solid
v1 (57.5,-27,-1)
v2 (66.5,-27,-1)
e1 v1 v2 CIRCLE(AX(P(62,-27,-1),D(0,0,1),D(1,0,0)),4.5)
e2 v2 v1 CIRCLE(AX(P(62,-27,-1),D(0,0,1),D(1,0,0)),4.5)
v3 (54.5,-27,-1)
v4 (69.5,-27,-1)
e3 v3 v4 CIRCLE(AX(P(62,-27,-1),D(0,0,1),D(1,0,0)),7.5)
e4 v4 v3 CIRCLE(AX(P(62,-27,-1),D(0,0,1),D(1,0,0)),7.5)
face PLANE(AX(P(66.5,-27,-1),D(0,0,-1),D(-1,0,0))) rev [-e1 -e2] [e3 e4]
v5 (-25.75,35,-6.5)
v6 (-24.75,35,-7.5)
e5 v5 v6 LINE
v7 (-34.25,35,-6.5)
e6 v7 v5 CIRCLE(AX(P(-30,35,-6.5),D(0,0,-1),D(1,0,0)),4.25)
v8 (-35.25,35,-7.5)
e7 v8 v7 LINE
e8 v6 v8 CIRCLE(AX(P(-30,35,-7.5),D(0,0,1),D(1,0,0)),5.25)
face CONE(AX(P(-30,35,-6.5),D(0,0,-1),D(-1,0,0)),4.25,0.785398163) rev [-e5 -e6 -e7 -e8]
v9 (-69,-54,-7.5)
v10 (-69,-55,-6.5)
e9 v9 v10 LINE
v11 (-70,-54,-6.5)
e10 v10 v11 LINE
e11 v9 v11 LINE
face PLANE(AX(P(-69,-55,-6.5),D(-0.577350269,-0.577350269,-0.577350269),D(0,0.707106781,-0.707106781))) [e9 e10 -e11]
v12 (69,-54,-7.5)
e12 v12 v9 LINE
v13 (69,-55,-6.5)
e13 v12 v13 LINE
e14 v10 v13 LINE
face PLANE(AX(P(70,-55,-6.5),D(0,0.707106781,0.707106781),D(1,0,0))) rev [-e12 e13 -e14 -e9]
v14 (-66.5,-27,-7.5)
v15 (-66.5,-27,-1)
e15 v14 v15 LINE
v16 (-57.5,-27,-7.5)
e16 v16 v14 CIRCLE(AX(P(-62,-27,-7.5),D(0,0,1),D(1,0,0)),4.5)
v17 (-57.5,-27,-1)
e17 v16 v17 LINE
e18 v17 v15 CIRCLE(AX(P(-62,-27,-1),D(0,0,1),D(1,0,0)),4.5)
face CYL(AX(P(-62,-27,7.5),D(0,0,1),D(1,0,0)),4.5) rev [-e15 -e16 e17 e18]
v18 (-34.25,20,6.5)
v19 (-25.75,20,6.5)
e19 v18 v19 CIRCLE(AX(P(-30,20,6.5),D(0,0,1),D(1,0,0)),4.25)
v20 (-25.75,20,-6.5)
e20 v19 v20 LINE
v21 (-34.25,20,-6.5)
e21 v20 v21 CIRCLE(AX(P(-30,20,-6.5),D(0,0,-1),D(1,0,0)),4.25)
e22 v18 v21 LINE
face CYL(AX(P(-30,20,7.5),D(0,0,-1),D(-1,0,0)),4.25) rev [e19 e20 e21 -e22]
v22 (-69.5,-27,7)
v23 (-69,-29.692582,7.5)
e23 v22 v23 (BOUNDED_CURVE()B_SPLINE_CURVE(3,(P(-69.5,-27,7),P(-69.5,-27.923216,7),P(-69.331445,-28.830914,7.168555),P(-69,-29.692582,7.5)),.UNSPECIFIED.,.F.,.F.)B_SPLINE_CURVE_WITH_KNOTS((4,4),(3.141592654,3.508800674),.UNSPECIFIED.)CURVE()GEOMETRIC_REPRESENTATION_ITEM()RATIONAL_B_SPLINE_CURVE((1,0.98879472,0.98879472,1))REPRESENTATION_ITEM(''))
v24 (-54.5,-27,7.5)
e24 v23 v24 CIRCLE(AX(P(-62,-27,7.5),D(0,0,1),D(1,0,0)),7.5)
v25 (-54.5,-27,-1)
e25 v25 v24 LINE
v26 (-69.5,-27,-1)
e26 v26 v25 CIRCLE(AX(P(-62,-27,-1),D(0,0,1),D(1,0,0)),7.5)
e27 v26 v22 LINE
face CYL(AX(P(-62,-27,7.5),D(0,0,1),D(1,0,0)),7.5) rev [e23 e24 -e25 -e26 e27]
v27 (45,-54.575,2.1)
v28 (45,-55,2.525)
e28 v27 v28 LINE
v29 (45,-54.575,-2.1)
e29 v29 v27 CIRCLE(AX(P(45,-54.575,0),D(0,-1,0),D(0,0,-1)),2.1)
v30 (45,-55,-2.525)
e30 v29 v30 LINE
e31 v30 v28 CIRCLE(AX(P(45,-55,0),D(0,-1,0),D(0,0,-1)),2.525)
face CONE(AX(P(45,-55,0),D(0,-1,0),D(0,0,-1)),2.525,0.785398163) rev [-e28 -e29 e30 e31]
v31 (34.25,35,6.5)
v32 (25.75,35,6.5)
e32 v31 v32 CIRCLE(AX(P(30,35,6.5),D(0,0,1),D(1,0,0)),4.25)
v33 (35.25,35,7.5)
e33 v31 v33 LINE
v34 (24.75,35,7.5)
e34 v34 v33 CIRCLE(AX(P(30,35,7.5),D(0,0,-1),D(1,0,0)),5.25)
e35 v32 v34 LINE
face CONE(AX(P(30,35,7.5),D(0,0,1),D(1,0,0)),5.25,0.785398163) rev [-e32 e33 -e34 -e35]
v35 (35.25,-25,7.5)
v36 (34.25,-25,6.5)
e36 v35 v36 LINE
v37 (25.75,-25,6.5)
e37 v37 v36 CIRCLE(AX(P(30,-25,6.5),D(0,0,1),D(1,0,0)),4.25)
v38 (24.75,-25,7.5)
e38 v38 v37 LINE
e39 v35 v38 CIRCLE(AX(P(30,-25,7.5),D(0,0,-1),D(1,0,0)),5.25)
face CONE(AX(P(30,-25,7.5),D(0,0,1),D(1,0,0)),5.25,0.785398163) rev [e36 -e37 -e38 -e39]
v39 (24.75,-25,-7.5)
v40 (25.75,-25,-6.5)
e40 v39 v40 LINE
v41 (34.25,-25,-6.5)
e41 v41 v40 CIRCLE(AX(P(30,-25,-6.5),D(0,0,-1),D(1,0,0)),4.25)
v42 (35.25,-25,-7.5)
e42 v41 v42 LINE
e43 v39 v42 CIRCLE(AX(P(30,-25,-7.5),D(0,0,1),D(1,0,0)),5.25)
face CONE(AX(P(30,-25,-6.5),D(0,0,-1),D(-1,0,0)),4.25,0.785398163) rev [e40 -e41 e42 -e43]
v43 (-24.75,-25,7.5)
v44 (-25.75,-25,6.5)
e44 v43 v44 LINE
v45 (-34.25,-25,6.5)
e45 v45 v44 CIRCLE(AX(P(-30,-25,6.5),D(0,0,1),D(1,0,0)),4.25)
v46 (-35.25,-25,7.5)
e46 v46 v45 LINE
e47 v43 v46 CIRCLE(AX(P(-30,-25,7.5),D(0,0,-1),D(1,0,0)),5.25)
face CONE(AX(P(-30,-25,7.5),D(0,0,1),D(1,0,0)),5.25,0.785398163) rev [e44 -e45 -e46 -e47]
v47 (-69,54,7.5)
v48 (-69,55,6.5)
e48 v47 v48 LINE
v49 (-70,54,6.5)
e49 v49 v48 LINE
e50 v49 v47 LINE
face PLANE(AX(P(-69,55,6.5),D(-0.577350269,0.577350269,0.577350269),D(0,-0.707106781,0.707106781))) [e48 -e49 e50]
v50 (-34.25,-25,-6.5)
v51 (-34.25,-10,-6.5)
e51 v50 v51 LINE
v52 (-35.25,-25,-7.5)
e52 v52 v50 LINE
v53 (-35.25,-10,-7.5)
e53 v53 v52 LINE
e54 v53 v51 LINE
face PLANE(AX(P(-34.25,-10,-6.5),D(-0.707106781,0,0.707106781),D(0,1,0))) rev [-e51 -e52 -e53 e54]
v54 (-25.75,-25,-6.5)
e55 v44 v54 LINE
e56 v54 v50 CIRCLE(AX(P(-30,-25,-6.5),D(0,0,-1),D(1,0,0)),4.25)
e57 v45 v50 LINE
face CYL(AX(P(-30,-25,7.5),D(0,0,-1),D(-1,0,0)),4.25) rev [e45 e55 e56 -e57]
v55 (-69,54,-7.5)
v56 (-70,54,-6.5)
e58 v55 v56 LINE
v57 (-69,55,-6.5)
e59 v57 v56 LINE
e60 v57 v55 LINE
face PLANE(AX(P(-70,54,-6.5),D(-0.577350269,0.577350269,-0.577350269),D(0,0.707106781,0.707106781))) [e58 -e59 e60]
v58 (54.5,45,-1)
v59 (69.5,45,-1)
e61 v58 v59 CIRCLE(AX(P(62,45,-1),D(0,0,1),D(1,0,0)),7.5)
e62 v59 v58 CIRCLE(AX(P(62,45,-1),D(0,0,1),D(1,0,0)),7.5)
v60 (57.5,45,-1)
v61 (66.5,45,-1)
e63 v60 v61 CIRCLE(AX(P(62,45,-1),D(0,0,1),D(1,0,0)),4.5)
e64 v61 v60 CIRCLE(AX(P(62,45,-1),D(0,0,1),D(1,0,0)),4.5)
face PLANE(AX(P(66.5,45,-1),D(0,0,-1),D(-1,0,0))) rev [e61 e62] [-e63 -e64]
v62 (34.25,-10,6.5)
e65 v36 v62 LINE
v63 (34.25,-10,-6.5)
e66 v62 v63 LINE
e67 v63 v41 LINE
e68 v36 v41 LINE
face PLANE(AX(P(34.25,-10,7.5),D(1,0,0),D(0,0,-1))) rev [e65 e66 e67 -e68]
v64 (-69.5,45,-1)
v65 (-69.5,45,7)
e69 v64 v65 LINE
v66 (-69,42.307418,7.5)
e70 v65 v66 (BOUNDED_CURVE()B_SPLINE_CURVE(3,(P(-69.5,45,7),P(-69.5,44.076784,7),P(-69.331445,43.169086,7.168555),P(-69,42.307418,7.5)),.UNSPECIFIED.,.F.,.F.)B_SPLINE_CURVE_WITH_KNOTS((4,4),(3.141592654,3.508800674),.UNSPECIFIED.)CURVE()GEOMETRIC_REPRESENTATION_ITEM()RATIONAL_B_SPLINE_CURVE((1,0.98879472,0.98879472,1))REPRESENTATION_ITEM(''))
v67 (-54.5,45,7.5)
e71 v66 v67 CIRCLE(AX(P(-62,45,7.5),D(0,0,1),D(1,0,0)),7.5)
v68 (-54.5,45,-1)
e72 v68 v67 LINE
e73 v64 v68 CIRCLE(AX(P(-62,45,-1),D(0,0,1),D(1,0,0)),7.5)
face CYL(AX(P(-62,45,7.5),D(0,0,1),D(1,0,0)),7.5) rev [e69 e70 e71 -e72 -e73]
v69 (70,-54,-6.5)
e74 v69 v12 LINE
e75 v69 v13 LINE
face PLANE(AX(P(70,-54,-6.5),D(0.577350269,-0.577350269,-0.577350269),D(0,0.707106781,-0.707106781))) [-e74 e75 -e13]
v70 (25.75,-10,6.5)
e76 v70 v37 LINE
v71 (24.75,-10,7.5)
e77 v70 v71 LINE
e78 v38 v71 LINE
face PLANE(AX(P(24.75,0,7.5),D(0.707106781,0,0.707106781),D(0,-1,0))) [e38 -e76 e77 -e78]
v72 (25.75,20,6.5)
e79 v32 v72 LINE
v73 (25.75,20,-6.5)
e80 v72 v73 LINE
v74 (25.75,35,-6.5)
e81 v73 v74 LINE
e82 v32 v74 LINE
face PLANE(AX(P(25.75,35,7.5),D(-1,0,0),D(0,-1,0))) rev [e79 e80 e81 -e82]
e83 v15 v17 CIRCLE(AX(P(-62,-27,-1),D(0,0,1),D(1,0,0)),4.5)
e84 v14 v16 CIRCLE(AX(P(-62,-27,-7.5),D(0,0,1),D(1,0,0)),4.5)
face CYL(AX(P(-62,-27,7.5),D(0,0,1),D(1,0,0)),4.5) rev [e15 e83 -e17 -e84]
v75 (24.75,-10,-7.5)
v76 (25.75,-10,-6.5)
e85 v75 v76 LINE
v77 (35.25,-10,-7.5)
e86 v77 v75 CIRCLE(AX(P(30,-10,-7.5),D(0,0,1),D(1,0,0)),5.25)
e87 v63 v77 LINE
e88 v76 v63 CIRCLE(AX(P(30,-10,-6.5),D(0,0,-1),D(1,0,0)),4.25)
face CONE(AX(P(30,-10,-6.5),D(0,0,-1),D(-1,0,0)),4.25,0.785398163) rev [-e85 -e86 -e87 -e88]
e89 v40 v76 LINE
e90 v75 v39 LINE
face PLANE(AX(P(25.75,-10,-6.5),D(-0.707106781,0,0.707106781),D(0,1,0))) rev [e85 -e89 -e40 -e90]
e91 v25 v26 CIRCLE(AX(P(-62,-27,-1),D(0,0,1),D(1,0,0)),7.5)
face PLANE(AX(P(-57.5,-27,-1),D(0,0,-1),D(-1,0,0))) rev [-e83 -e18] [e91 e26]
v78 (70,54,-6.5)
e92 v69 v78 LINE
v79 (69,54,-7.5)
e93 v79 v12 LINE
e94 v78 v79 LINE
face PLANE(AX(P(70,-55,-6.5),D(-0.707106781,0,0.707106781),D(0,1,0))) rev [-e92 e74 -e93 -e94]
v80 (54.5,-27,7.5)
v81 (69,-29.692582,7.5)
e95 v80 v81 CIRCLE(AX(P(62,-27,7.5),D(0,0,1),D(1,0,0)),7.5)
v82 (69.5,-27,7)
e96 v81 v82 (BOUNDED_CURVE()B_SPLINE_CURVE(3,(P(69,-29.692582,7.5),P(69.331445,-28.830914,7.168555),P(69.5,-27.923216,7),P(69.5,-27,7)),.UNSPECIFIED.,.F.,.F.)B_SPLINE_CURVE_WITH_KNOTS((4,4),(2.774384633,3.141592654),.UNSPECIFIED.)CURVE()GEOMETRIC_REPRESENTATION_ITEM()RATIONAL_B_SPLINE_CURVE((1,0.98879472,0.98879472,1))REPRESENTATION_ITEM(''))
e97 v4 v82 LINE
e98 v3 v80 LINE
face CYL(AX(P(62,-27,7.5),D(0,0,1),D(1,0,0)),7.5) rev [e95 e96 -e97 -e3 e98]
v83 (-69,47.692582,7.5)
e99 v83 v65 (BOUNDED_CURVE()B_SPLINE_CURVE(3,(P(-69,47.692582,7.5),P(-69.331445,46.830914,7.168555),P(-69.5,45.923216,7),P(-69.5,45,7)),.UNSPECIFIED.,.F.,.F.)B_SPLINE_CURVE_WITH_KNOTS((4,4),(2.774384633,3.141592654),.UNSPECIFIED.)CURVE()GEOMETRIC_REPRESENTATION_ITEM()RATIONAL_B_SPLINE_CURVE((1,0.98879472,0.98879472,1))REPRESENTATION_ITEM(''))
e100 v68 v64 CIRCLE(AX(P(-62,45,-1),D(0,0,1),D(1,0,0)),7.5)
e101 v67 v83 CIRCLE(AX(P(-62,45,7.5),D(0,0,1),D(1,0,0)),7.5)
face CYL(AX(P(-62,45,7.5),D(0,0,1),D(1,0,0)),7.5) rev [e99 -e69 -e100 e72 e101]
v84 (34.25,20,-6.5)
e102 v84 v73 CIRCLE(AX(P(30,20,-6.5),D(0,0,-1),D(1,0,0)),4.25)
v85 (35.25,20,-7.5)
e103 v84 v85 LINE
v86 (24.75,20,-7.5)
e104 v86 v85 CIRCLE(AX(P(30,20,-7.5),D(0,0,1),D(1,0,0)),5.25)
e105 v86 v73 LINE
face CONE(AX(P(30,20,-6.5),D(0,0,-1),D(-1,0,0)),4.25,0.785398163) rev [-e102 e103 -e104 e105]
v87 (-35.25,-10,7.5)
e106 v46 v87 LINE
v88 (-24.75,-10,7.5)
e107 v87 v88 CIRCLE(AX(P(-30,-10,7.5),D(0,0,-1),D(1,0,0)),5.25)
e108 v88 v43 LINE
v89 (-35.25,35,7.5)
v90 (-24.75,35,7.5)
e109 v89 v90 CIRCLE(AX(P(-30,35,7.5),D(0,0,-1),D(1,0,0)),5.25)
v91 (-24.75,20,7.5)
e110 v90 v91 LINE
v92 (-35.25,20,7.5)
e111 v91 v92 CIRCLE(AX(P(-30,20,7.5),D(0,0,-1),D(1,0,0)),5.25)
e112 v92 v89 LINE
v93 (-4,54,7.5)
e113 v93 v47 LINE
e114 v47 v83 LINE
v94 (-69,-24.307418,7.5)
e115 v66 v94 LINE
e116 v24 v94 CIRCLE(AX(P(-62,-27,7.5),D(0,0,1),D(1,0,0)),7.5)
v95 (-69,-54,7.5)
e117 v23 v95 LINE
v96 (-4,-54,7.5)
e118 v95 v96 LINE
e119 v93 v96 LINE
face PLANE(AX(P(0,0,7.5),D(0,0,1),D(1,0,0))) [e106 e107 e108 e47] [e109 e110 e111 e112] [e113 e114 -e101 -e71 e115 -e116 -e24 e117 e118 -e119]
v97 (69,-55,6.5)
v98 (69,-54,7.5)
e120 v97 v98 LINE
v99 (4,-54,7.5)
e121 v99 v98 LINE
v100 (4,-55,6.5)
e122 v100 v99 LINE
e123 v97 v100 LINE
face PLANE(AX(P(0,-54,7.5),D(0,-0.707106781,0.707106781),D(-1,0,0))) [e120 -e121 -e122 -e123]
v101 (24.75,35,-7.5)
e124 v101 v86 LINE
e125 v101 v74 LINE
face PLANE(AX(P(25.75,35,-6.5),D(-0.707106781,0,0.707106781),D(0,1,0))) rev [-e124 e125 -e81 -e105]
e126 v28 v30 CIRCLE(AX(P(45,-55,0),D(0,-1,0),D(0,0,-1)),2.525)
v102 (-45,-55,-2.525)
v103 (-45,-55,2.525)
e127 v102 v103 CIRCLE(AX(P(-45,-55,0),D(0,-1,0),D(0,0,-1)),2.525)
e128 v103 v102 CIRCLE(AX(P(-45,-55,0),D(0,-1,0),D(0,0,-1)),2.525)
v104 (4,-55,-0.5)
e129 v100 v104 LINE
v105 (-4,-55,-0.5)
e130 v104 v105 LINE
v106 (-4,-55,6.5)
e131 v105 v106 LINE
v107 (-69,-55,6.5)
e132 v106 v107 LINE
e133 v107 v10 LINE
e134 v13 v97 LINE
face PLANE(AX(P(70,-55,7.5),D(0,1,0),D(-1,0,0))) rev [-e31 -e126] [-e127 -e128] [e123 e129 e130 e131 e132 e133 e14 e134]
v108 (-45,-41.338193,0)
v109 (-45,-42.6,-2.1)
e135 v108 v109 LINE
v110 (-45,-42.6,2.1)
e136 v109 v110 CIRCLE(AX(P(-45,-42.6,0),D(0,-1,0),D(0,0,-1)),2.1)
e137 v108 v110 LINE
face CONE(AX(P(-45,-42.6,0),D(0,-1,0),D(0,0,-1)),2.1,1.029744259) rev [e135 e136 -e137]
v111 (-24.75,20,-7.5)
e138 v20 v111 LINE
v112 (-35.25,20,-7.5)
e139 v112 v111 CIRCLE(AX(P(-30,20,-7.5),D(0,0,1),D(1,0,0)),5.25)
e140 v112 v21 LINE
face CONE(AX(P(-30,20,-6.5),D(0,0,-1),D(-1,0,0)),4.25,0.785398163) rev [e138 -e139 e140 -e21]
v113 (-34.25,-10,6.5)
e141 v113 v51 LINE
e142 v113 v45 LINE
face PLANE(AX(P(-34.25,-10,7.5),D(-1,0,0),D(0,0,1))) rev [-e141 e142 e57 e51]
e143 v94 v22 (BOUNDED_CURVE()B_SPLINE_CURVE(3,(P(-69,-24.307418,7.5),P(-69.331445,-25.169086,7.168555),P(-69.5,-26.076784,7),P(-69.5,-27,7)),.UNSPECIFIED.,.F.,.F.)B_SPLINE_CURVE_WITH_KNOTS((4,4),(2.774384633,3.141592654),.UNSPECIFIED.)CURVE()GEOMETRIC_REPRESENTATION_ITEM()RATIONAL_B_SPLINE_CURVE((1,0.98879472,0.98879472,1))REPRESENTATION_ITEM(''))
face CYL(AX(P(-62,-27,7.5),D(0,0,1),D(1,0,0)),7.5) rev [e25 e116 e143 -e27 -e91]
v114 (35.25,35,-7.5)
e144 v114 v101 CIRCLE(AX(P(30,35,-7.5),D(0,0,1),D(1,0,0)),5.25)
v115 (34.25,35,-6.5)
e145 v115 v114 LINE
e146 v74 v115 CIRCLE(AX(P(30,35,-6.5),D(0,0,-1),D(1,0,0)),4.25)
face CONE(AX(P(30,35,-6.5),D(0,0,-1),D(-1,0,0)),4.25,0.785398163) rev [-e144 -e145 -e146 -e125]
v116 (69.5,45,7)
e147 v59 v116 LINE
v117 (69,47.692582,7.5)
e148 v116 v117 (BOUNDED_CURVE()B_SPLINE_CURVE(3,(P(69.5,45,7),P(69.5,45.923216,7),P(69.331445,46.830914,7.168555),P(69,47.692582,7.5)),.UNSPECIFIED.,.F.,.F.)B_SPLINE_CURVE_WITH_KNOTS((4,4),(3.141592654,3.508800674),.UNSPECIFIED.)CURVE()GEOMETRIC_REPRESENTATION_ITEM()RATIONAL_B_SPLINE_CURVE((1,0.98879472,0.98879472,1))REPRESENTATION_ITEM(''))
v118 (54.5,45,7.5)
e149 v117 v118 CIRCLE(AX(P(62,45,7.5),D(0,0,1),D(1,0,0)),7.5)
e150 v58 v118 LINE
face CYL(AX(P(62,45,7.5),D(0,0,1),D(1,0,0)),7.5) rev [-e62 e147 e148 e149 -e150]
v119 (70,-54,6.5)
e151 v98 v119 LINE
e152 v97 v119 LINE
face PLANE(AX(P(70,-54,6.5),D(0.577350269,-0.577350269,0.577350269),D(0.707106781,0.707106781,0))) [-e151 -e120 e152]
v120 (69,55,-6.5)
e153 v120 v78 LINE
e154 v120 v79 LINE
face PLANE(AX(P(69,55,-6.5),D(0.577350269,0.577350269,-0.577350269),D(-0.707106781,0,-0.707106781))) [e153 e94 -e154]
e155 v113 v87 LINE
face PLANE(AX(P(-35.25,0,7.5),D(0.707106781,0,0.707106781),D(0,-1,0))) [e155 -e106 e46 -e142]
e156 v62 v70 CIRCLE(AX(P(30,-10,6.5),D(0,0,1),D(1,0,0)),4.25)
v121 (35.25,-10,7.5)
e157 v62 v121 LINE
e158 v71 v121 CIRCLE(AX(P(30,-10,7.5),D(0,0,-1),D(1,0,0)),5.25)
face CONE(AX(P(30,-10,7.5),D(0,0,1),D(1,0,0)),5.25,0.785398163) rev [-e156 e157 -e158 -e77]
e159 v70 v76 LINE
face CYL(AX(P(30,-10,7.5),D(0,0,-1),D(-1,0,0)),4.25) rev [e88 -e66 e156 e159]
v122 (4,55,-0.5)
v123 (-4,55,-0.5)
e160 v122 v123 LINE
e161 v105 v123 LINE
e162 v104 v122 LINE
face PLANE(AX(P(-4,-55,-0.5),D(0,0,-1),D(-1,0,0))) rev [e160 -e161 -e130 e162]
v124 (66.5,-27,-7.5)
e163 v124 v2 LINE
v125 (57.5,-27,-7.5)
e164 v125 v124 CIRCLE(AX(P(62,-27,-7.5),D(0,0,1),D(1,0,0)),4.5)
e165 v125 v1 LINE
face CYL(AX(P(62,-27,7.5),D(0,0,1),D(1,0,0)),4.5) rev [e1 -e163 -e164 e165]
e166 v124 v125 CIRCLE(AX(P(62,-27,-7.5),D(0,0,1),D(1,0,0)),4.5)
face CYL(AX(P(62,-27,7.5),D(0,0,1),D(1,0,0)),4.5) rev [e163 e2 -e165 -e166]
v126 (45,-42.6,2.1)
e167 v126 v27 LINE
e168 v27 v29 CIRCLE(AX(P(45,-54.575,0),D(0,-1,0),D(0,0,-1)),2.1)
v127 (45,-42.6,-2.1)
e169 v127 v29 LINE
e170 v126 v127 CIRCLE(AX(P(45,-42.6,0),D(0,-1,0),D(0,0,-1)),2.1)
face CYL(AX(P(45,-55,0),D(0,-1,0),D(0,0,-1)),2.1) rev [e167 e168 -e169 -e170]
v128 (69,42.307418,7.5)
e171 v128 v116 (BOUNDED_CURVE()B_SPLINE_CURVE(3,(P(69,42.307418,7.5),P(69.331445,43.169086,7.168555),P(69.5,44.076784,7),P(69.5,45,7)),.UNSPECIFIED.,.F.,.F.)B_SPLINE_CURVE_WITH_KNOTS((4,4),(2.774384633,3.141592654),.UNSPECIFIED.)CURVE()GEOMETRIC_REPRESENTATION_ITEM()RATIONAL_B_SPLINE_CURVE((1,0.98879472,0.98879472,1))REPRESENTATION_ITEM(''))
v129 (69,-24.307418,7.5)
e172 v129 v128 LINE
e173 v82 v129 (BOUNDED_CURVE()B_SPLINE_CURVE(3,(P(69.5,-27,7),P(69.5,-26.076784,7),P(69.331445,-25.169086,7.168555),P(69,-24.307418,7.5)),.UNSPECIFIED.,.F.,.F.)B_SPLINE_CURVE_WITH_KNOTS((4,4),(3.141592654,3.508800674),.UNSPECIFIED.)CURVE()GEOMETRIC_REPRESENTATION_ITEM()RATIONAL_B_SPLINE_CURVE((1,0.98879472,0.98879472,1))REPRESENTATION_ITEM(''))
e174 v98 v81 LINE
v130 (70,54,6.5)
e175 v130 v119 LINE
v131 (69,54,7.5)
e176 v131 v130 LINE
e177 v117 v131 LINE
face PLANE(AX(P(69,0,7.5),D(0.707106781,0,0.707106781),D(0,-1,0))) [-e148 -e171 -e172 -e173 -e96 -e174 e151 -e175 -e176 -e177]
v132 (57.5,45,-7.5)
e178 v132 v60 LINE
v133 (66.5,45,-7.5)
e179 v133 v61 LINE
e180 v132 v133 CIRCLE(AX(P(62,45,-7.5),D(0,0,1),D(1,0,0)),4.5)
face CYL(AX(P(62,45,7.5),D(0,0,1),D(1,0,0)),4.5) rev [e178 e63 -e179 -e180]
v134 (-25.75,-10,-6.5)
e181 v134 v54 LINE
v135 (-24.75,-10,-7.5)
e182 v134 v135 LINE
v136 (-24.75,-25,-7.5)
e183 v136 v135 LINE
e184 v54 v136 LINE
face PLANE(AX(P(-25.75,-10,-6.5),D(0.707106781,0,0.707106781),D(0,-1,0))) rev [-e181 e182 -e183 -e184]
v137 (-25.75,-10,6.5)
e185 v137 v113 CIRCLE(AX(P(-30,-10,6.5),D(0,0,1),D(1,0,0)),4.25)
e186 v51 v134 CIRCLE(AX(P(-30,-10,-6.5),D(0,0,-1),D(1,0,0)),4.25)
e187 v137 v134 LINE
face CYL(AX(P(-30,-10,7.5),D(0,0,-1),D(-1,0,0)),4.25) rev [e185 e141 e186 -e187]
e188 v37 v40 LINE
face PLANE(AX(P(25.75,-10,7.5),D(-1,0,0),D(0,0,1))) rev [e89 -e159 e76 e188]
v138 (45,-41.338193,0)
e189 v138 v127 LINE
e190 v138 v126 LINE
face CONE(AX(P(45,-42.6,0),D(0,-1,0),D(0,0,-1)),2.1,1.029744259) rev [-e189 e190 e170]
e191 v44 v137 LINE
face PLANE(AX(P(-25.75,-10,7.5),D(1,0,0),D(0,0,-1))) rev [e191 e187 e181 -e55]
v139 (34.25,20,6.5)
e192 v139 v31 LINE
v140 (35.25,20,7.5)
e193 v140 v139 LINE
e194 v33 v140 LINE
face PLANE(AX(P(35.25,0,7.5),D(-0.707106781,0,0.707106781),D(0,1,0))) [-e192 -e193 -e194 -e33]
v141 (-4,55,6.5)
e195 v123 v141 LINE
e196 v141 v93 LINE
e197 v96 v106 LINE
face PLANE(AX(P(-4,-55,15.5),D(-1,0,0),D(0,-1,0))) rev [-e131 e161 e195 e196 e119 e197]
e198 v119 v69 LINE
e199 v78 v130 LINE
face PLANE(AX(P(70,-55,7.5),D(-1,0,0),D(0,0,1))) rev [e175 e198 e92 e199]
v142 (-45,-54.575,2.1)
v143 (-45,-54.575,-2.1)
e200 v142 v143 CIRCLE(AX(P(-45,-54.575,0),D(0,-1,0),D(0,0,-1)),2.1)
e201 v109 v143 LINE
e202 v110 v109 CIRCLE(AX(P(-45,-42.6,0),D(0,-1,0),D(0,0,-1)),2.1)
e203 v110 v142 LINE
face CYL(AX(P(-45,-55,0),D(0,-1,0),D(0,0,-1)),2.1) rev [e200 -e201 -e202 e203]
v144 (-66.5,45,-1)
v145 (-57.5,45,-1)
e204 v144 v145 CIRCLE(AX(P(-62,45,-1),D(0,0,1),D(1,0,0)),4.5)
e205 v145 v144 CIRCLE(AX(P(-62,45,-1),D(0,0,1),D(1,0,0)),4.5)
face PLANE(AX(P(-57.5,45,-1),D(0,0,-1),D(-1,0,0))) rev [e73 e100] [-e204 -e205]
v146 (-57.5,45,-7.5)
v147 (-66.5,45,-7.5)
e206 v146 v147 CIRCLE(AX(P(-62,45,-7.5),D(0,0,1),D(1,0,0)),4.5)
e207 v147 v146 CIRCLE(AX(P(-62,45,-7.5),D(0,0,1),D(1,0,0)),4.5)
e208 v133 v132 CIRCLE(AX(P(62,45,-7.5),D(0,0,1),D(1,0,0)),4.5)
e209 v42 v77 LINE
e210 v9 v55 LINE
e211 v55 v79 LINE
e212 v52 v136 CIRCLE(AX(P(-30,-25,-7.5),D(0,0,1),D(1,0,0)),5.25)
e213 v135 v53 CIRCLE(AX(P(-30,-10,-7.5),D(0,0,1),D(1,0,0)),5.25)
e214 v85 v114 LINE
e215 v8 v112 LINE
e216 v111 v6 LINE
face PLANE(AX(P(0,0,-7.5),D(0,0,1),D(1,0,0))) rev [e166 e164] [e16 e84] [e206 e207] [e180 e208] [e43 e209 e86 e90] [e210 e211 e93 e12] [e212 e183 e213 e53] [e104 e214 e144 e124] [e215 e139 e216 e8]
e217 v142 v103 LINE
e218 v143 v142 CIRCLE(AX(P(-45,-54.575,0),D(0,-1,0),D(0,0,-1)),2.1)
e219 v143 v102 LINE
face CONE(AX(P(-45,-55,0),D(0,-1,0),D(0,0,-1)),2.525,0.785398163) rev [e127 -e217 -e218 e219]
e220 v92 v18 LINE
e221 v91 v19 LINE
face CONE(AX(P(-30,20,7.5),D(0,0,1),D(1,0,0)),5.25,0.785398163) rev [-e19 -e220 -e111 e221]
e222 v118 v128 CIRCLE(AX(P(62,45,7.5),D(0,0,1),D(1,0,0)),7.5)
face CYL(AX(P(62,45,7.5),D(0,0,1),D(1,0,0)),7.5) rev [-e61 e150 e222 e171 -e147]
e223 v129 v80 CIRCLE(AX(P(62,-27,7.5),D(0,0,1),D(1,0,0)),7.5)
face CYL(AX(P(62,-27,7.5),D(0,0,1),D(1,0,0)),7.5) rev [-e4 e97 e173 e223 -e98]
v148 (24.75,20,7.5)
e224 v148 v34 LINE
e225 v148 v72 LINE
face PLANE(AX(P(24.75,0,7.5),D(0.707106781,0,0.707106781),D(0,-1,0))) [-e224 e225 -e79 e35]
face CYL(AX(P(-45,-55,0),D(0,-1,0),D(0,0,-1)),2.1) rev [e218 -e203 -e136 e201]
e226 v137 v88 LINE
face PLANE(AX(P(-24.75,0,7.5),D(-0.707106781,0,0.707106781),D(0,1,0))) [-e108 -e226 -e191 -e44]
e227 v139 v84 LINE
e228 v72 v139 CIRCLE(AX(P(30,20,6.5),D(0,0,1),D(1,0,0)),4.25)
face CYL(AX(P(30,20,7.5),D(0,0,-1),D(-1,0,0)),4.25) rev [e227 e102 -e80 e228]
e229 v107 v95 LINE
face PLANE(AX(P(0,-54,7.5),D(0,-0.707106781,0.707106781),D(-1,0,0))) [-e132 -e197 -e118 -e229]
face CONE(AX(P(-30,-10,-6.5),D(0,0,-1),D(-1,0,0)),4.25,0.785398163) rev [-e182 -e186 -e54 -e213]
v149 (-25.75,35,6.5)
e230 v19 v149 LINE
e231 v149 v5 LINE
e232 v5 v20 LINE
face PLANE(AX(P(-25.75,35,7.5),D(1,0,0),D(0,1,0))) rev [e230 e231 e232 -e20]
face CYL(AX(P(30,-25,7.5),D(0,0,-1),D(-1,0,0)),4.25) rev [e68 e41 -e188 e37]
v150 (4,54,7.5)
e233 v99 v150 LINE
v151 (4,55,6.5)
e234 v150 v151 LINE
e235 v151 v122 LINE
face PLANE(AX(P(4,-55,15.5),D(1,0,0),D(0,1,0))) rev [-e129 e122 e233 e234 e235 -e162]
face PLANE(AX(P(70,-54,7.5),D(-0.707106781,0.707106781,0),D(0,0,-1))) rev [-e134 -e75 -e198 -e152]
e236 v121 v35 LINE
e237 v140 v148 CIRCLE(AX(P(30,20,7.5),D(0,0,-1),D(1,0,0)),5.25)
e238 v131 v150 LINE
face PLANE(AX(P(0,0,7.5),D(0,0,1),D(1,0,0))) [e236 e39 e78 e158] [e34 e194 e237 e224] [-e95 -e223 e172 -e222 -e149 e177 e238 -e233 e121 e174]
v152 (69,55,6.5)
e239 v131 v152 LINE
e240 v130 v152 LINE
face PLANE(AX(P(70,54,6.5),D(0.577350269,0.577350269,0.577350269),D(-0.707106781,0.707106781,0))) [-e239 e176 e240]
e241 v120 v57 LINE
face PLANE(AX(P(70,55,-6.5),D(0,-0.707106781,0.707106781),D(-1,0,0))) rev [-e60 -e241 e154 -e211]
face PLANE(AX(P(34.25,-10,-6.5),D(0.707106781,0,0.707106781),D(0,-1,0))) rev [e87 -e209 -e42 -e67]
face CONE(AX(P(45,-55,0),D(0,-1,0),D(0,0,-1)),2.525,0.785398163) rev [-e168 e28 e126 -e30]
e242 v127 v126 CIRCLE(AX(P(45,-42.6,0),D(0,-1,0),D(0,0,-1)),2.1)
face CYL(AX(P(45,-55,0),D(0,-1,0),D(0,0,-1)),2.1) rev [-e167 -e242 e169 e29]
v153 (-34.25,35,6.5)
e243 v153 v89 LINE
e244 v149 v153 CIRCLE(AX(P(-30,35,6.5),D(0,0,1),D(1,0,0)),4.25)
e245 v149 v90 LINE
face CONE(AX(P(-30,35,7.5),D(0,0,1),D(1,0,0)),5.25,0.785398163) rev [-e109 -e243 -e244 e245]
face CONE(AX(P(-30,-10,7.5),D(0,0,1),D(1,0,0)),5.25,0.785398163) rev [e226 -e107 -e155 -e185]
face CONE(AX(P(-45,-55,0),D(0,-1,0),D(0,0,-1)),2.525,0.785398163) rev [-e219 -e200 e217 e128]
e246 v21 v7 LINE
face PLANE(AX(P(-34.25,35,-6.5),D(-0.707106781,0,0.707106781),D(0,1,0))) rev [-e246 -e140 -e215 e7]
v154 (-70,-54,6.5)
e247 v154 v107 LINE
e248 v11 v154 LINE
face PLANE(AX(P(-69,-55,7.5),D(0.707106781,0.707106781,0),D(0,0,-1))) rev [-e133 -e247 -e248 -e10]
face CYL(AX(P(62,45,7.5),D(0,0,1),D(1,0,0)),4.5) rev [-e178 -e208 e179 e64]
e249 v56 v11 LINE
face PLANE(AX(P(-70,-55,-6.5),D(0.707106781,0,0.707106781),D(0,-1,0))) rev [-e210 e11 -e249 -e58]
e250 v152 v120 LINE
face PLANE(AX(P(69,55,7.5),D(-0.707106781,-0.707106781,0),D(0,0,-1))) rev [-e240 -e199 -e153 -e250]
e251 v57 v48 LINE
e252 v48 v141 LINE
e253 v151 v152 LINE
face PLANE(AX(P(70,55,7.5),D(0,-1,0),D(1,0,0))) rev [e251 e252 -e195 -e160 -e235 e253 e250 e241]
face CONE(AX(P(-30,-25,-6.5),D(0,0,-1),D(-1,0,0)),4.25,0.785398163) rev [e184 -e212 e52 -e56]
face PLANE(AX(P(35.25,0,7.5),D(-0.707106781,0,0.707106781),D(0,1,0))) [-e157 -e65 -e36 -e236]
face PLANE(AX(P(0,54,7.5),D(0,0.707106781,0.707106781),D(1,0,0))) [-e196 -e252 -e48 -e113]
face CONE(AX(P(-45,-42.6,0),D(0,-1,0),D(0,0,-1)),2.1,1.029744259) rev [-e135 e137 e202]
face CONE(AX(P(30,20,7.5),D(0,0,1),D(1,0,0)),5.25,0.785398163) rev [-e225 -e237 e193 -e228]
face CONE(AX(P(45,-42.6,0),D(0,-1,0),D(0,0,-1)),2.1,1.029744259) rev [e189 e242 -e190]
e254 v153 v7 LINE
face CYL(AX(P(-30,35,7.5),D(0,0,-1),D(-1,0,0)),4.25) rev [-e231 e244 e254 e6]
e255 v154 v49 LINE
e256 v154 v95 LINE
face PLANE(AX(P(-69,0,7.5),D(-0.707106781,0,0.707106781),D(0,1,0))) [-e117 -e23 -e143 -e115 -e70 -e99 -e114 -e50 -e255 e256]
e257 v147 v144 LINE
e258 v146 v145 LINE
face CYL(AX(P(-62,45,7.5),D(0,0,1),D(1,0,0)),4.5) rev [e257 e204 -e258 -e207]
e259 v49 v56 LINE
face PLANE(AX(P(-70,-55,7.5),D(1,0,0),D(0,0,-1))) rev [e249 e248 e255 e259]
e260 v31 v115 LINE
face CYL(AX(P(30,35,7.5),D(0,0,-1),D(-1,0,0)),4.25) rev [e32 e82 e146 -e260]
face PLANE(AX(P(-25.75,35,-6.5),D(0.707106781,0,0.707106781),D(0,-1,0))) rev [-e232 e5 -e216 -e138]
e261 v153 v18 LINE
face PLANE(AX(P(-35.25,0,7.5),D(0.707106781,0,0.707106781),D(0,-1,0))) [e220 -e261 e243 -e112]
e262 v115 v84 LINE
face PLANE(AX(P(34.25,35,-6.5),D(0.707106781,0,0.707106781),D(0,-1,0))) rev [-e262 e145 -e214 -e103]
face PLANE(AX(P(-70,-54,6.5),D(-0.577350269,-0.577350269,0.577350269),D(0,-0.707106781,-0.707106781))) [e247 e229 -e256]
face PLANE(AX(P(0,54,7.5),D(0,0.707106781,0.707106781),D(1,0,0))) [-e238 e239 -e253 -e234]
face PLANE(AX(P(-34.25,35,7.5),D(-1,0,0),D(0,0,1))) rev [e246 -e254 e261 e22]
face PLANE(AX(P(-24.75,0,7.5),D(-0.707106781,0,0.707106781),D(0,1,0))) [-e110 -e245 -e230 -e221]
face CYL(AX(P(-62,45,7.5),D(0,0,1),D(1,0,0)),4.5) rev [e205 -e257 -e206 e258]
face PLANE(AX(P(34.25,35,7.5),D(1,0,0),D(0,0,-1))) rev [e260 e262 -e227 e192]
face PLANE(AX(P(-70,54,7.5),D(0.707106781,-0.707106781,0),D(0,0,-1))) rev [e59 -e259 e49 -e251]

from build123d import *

# Parameters (mm, degrees)
SKETCH_1_W                   = 140
SKETCH_1_H                   = 110
EXTRUDE_1_DEPTH              = 7.5
CUT_EXTRUDE_1_DEPTH          = 91.277350426
CHAMFER_2_SIZE               = 1
SKETCH_5_W                   = 8
SKETCH_5_H                   = 16
CUT_EXTRUDE_2_DEPTH          = 131.599578866
HOLE_WIZARD_M5_1_D           = 4.2
HOLE_WIZARD_M5_2_D           = 4.2
HOLE_WIZARD_M5_2_DEPTH       = 12.4
HOLE_WIZARD_M5_2_CSINK_D     = 5.05
HOLE_WIZARD_M5_2_CSINK_ANGLE = 90
HOLE_WIZARD_M5_2_TIP         = 1.2618073
HOLE1_D                      = 9
HOLE1_CBORE_D                = 15
HOLE1_CBORE_DEPTH            = 8.5


with BuildPart() as part:
    # 草图1 → 凸台-拉伸1 (new, symmetric)
    with BuildSketch(Plane.XY):
        Rectangle(SKETCH_1_W, SKETCH_1_H)
    extrude(amount=EXTRUDE_1_DEPTH, both=True)

    # 草图4 → 切除-拉伸1 (cut, through all)
    with BuildSketch(Plane(origin=(0, 0, -7.5), x_dir=(-1, 0, 0), z_dir=(0, 0, -1))):
        with BuildLine():
            Line((-25.75, -10), (-25.75, -25))
            ThreePointArc((-25.75, -25), (-30, -29.25), (-34.25, -25))
            Line((-34.25, -25), (-34.25, -10))
            ThreePointArc((-34.25, -10), (-30, -5.75), (-25.75, -10))
        make_face()
        with BuildLine():
            Line((-25.75, 35), (-25.75, 20))
            ThreePointArc((-25.75, 20), (-30, 15.75), (-34.25, 20))
            Line((-34.25, 20), (-34.25, 35))
            ThreePointArc((-34.25, 35), (-30, 39.25), (-25.75, 35))
        make_face()
        with BuildLine():
            Line((25.75, 35), (25.75, 20))
            ThreePointArc((25.75, 20), (30, 15.75), (34.25, 20))
            Line((34.25, 20), (34.25, 35))
            ThreePointArc((34.25, 35), (30, 39.25), (25.75, 35))
        make_face()
        with BuildLine():
            Line((25.75, -10), (25.75, -25))
            ThreePointArc((25.75, -25), (30, -29.25), (34.25, -25))
            Line((34.25, -25), (34.25, -10))
            ThreePointArc((34.25, -10), (30, -5.75), (25.75, -10))
        make_face()
    extrude(amount=-CUT_EXTRUDE_1_DEPTH, mode=Mode.SUBTRACT)

    # 倒角2
    chamfer_2_edges = [part.edges().sort_by_distance(p)[0] for p in [
        (70, 0, 7.5),
        (0, 55, 7.5),
        (30, -5.75, 7.5),
        (25.75, -17.5, 7.5),
        (30, -29.25, 7.5),
        (34.25, -17.5, 7.5),
        (30, -5.75, -7.5),
        (34.25, -17.5, -7.5),
        (30, -29.25, -7.5),
        (25.75, -17.5, -7.5),
        (30, 39.25, 7.5),
        (25.75, 27.5, 7.5),
        (-70, 0, 7.5),
        (30, 15.75, 7.5),
        (34.25, 27.5, 7.5),
        (30, 39.25, -7.5),
        (34.25, 27.5, -7.5),
        (30, 15.75, -7.5),
        (25.75, 27.5, -7.5),
        (0, 55, -7.5),
        (-30, 39.25, 7.5),
        (-34.25, 27.5, 7.5),
        (-30, 15.75, 7.5),
        (-25.75, 27.5, 7.5),
        (-30, 39.25, -7.5),
        (-25.75, 27.5, -7.5),
        (-30, 15.75, -7.5),
        (-34.25, 27.5, -7.5),
        (70, 0, -7.5),
        (-30, -5.75, 7.5),
        (-34.25, -17.5, 7.5),
        (-30, -29.25, 7.5),
        (-25.75, -17.5, 7.5),
        (-30, -5.75, -7.5),
        (-25.75, -17.5, -7.5),
        (0, -55, -7.5),
        (-30, -29.25, -7.5),
        (-34.25, -17.5, -7.5),
        (-70, 0, -7.5),
        (0, -55, 7.5),
        (-70, 55, 0),
        (70, 55, 0),
        (70, -55, 0),
        (-70, -55, 0),
    ]]
    chamfer(chamfer_2_edges, length=CHAMFER_2_SIZE)

    # 草图5 → 切除-拉伸2 (cut, through all)
    with BuildSketch(Plane(origin=(0, 55, 0), x_dir=(1, 0, 0), z_dir=(0, 1, 0))):
        with Locations((0, -7.5)):
            Rectangle(SKETCH_5_W, SKETCH_5_H)
    extrude(amount=-CUT_EXTRUDE_2_DEPTH, mode=Mode.SUBTRACT)

    # M5 螺纹孔1 (through all)
    with Locations(Plane(origin=(0, 0, -7.5), x_dir=(-1, 0, 0), z_dir=(0, 0, -1))):
        with Locations((-62, 45), (-62, -27), (62, -27), (62, 45)):
            Hole(HOLE_WIZARD_M5_1_D / 2)

    # M5 螺纹孔2
    with Locations(Plane(origin=(0, -55, 0), x_dir=(-1, 0, 0), z_dir=(0, -1, 0))):
        with Locations((45, 0), (-45, 0)):
            CounterSinkHole(HOLE_WIZARD_M5_2_D / 2, HOLE_WIZARD_M5_2_CSINK_D / 2, depth=HOLE_WIZARD_M5_2_DEPTH, counter_sink_angle=HOLE_WIZARD_M5_2_CSINK_ANGLE)
            with Locations((0, 0, -(HOLE_WIZARD_M5_2_DEPTH + HOLE_WIZARD_M5_2_TIP / 2))):  # 118° drill point
                Cone(0, HOLE_WIZARD_M5_2_D / 2, HOLE_WIZARD_M5_2_TIP, mode=Mode.SUBTRACT)

    # Hole1 (through all)
    with Locations(Plane(origin=(49.130892878, -26.065000019, 7.5), x_dir=(1, 0, 0), z_dir=(0, 0, 1))):
        with Locations((12.869107122, -0.934999981), (12.869107122, 71.065000019), (-111.130892878, 71.065000019), (-111.130892878, -0.934999981)):
            CounterBoreHole(HOLE1_D / 2, HOLE1_CBORE_D / 2, HOLE1_CBORE_DEPTH)


solid = part.part
